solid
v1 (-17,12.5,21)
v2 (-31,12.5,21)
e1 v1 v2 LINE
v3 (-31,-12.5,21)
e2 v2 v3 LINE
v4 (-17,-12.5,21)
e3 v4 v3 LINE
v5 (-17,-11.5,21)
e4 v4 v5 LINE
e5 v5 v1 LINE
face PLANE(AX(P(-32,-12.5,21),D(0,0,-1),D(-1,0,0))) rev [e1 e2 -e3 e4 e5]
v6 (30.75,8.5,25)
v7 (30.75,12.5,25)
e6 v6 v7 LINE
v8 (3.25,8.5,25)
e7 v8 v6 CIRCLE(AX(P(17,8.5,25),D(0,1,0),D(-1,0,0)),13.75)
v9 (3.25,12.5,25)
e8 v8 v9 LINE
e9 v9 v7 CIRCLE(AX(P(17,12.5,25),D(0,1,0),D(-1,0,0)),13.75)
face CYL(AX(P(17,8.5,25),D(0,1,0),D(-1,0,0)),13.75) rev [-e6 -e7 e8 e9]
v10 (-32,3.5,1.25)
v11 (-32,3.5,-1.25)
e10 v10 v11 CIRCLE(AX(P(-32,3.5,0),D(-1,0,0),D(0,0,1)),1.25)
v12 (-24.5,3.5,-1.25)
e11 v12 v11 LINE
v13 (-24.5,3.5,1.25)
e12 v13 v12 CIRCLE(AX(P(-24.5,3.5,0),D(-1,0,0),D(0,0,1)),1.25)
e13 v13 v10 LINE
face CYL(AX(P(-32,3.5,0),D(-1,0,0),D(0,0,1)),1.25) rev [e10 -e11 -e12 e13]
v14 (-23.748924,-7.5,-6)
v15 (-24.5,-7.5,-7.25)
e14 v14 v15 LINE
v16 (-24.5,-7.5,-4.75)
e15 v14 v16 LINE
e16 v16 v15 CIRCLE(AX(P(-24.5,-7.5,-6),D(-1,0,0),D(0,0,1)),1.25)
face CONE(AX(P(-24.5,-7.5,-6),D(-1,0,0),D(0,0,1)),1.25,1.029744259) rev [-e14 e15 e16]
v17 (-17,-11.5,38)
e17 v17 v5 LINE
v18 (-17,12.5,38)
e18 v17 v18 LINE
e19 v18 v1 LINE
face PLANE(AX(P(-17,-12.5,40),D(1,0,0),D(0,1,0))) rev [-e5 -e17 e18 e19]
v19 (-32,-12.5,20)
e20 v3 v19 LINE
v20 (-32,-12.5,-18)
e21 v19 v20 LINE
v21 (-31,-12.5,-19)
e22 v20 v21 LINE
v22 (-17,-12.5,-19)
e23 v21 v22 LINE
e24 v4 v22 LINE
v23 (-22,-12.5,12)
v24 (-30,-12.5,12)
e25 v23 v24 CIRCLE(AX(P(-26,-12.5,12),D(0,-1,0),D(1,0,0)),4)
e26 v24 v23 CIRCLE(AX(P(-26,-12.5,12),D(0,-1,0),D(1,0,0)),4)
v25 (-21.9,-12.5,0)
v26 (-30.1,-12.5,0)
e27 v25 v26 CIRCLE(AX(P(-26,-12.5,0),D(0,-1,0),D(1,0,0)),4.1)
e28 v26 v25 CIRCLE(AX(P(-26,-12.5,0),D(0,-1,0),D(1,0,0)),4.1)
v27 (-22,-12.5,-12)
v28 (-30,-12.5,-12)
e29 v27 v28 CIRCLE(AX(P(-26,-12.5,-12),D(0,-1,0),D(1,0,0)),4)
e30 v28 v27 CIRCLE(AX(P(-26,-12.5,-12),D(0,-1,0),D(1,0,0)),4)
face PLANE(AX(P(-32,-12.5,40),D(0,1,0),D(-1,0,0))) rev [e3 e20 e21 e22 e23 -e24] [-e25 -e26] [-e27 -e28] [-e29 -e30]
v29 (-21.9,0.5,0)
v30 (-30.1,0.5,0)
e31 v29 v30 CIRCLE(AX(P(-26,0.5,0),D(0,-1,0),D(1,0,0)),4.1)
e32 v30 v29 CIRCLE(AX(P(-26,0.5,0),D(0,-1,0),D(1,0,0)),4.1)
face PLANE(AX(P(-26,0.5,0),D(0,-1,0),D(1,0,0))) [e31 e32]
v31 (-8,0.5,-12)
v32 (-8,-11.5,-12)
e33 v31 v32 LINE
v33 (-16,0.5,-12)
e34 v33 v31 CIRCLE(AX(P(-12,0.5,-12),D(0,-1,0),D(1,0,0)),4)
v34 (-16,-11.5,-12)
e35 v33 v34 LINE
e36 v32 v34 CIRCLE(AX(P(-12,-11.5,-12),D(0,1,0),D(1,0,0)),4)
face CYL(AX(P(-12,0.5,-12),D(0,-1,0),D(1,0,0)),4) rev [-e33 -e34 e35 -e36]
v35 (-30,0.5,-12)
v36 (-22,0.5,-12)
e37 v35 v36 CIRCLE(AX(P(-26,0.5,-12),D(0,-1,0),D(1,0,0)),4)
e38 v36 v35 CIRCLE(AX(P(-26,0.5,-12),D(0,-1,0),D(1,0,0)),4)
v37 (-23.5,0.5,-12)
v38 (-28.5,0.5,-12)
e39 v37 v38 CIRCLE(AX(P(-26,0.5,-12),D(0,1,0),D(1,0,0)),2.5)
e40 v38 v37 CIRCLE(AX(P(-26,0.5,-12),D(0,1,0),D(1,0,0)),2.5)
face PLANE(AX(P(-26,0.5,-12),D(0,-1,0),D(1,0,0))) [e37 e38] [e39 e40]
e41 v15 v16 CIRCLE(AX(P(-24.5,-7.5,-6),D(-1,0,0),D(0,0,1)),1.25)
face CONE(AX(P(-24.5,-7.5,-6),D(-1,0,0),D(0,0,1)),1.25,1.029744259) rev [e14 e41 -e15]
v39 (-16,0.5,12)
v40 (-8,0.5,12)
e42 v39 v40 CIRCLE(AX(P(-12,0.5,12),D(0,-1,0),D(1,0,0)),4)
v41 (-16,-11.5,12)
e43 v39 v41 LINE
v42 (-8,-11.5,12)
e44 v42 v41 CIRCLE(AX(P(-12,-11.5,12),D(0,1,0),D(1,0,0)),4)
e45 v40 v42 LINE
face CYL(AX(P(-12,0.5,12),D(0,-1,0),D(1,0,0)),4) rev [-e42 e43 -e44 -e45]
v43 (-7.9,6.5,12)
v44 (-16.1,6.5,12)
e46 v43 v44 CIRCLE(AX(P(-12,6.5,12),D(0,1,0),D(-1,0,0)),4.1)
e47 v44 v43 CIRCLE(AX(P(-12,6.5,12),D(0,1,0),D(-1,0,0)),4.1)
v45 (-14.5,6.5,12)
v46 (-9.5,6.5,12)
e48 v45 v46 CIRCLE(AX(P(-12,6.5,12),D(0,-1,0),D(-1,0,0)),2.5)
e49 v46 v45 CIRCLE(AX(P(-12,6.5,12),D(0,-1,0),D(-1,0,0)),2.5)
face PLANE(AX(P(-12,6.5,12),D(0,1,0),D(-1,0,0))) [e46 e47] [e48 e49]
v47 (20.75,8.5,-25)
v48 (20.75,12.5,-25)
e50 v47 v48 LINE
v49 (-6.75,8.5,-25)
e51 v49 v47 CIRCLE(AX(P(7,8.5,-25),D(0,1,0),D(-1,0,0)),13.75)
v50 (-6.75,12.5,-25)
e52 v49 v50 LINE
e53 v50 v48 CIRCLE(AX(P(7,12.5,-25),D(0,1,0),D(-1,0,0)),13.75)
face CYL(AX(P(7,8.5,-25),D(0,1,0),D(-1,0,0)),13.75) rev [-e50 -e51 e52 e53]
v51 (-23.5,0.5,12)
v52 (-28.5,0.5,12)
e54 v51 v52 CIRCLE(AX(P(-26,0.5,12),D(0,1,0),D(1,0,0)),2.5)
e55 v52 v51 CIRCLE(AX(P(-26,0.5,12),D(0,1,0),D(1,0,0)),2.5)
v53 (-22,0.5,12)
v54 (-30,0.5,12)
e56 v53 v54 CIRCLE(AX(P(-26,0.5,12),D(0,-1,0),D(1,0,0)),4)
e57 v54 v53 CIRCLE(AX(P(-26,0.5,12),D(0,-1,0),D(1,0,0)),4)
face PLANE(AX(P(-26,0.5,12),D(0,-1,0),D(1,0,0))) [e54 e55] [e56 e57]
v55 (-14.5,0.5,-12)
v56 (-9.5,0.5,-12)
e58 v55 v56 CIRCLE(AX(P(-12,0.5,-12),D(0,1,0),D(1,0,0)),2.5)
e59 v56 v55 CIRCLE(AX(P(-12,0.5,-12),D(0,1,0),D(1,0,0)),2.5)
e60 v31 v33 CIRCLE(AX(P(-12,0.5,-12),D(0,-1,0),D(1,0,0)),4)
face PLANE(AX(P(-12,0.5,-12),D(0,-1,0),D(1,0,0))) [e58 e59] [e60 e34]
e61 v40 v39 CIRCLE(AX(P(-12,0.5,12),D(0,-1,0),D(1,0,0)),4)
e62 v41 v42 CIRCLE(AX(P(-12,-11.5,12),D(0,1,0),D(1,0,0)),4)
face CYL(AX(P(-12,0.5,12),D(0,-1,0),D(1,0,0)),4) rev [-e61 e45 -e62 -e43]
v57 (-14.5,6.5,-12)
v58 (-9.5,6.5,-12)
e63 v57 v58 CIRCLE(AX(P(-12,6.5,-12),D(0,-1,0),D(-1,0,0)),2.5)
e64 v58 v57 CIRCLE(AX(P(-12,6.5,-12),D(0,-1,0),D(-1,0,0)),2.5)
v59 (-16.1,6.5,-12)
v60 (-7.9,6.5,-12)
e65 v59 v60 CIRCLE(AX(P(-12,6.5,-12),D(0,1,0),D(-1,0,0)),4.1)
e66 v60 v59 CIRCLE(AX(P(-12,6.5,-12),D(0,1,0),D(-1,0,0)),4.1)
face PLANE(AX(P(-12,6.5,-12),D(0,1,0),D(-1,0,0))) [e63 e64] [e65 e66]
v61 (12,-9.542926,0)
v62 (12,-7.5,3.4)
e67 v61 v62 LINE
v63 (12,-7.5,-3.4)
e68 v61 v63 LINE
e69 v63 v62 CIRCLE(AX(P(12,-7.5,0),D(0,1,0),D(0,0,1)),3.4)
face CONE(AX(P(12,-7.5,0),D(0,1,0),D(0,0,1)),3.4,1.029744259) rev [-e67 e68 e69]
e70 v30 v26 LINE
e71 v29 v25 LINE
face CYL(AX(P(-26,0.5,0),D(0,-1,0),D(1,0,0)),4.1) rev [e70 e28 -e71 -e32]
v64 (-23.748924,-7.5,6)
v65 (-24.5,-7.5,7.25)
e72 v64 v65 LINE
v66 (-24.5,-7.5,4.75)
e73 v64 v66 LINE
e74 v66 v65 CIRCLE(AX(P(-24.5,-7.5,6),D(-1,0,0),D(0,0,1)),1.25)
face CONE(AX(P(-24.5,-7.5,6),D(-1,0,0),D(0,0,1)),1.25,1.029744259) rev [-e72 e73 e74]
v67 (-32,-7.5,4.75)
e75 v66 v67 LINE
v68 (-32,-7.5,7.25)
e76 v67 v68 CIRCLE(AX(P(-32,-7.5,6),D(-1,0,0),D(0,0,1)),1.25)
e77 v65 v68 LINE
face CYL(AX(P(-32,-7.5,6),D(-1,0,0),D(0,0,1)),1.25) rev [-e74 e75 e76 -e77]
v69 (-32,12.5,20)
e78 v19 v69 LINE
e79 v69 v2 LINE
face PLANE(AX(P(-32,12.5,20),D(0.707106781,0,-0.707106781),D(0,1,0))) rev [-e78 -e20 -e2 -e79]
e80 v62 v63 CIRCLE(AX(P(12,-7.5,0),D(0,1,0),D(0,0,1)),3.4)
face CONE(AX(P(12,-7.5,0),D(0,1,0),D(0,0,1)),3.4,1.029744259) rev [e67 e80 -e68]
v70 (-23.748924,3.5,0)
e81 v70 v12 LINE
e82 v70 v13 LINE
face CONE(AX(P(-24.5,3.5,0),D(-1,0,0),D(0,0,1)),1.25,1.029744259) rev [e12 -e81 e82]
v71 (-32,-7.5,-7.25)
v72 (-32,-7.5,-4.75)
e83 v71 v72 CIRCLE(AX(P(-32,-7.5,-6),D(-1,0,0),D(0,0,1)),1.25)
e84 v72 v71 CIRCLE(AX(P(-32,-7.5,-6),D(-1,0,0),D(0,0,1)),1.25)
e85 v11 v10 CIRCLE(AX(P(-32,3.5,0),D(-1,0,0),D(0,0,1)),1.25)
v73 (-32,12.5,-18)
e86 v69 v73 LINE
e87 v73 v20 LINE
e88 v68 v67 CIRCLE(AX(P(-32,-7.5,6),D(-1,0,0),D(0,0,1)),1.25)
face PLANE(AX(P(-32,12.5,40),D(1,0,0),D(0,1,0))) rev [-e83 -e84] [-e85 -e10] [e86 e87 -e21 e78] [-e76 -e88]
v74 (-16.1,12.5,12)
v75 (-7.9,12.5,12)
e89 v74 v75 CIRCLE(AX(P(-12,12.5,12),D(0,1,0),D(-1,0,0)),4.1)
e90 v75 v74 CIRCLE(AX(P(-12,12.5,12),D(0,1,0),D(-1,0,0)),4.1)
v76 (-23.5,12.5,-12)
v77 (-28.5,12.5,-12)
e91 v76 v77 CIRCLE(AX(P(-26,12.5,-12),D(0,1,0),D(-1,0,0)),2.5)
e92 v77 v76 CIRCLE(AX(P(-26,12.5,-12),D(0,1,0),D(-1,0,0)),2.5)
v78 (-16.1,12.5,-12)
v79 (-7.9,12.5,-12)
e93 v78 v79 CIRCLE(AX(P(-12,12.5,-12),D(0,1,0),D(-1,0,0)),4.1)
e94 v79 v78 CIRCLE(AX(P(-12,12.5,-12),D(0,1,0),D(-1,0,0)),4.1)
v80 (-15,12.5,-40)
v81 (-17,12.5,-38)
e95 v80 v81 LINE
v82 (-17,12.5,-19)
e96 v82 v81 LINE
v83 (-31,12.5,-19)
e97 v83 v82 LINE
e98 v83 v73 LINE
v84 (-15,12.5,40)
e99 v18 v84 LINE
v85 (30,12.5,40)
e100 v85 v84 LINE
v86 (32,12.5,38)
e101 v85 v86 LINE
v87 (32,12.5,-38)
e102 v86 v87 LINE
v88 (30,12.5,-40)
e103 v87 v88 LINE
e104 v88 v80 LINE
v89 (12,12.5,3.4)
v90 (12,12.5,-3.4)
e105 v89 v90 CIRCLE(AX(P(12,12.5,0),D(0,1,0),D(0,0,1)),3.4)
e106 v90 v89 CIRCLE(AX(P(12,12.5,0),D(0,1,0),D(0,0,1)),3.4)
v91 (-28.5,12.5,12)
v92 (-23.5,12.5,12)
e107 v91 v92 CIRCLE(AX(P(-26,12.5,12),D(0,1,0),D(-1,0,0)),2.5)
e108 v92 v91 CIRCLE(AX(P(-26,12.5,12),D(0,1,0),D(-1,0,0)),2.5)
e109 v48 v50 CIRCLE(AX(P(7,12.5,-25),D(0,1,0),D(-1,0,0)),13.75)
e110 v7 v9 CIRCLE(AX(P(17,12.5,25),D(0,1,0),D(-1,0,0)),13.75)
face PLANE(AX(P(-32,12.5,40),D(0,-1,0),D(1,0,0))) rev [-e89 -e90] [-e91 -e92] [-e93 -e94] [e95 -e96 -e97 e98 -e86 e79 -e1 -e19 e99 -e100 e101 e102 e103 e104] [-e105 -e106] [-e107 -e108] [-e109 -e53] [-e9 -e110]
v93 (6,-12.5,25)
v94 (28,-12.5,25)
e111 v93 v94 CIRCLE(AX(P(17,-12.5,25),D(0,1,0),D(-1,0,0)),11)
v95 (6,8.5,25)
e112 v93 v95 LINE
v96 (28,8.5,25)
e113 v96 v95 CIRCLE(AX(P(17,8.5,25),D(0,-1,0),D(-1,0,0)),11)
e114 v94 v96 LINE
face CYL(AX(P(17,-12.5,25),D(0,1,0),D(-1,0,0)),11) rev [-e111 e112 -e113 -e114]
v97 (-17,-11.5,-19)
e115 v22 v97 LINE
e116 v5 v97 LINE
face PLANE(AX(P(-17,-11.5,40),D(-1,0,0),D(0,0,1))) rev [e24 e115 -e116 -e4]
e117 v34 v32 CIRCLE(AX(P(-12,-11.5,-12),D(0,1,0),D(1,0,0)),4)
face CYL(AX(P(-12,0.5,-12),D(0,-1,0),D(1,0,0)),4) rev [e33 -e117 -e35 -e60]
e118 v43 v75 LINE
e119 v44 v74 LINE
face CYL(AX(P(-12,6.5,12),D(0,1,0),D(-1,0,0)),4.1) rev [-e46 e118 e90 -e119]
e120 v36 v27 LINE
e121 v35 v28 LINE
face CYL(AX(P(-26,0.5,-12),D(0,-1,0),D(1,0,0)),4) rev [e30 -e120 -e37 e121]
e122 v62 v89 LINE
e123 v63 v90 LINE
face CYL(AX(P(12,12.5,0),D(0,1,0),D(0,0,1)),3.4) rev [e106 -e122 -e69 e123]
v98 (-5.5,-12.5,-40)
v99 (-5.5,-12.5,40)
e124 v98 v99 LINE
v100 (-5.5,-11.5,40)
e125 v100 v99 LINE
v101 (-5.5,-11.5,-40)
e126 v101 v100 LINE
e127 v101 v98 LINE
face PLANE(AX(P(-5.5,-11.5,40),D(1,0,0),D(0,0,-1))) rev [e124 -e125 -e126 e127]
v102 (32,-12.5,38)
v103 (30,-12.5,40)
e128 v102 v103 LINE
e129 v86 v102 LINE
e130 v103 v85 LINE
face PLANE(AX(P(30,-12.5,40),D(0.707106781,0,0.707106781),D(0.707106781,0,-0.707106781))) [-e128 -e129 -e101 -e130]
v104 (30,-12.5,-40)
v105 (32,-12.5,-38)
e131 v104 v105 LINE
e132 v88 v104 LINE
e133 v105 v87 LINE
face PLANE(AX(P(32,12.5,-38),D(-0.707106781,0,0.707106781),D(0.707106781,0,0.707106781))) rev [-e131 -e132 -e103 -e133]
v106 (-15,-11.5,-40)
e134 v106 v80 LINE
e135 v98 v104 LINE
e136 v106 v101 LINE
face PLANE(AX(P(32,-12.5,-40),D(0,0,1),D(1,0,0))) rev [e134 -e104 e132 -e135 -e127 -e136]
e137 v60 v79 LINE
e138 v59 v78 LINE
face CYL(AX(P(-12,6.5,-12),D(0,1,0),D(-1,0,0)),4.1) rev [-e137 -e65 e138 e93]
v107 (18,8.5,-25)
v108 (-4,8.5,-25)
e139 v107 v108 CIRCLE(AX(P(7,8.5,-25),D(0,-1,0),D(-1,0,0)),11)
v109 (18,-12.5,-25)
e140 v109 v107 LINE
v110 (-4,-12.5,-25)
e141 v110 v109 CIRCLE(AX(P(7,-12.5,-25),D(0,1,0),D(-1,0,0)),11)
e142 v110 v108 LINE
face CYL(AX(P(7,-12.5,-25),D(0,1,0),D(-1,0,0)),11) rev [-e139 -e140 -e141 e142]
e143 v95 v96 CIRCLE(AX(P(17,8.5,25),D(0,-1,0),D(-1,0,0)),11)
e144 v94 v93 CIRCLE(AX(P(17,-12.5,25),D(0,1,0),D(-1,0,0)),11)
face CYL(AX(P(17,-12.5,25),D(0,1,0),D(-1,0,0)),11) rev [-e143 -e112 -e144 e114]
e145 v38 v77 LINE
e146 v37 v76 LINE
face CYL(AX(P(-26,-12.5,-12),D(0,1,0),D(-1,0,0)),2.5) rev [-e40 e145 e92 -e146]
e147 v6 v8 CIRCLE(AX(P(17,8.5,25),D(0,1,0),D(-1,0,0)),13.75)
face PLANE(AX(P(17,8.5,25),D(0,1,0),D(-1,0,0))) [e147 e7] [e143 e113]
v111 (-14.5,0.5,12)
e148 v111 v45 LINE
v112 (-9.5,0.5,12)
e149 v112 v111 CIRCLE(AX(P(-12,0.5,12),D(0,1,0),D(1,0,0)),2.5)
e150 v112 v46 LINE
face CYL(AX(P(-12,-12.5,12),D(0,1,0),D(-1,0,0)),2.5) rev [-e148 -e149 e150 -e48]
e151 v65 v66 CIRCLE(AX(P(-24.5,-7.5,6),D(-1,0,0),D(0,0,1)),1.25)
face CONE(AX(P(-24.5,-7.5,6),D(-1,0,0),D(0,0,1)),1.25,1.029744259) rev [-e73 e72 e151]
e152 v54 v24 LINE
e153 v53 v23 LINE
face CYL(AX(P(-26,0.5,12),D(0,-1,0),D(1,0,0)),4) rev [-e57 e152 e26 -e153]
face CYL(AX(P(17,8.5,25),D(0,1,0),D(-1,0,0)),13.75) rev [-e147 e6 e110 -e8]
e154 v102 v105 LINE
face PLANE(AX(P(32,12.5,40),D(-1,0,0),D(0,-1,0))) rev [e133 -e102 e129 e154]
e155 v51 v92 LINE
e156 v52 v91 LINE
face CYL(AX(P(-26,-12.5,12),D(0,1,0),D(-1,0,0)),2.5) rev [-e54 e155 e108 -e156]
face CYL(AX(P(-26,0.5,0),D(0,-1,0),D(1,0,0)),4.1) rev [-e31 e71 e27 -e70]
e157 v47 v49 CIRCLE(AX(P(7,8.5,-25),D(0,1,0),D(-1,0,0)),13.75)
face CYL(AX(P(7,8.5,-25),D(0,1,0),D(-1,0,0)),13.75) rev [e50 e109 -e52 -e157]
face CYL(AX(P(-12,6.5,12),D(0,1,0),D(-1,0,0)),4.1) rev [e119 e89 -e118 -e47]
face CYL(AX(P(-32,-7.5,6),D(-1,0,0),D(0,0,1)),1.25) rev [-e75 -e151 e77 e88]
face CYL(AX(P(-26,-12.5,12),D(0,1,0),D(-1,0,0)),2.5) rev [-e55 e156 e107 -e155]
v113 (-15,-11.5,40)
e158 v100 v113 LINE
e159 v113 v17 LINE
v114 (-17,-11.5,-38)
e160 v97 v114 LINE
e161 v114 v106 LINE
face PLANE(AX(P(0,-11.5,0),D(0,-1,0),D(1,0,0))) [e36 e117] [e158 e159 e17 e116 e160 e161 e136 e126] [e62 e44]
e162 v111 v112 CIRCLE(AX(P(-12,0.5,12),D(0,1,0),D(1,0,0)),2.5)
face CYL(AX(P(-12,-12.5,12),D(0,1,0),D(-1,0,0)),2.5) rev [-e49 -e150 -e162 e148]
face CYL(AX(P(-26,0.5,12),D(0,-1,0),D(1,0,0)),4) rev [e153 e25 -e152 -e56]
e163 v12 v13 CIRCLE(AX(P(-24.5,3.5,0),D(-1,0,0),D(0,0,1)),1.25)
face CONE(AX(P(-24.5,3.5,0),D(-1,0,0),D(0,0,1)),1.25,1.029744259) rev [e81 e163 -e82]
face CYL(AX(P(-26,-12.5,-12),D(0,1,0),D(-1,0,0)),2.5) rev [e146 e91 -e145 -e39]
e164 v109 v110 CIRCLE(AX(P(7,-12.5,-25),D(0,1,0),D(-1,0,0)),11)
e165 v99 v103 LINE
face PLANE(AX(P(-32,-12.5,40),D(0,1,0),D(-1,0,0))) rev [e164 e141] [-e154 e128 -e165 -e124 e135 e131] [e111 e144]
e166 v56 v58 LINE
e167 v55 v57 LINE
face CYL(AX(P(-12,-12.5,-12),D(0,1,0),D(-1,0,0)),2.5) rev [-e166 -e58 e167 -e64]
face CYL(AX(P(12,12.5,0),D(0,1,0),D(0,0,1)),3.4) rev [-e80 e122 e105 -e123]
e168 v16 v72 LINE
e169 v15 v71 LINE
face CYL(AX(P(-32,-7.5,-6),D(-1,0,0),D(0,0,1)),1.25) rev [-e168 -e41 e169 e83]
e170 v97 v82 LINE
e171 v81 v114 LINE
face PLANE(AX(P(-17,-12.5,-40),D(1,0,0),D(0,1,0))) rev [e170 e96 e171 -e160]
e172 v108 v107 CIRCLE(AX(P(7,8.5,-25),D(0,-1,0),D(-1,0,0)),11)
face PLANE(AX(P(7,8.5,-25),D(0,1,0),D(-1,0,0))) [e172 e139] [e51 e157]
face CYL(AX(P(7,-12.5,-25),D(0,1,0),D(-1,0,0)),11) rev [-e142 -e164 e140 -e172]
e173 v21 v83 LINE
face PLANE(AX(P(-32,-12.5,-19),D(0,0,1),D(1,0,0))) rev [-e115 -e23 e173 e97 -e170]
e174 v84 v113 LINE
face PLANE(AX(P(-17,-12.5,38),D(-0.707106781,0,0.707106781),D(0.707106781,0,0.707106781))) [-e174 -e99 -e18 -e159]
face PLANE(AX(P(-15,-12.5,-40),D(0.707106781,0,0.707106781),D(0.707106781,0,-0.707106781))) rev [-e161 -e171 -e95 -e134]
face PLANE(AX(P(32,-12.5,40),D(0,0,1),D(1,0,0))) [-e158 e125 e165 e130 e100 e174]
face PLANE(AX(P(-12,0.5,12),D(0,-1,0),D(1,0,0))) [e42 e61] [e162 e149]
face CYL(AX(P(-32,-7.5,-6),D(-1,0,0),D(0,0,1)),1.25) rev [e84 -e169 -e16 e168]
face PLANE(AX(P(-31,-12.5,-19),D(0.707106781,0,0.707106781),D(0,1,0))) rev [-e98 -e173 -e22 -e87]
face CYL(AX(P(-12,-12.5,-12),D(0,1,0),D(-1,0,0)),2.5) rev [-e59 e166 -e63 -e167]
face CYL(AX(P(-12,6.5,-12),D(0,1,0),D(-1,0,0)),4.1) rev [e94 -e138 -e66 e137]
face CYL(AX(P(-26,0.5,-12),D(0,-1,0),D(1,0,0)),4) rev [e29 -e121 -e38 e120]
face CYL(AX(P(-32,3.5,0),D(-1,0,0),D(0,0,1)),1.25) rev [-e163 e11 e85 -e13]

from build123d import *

# Parameters (mm, degrees)
SKETCH1_W             = 64
SKETCH1_H             = 25
BOSS_EXTRUDE1_DEPTH   = 40
SKETCH3_R             = 11
SKETCH3_R_2           = 2.5
CUT_EXTRUDE1_DEPTH    = 58
M3_TAPPED_HOLE1_D     = 2.5
M3_TAPPED_HOLE1_DEPTH = 7.5
M3_TAPPED_HOLE1_TIP   = 0.751075774
M8_TAPPED_HOLE1_D     = 6.8
M8_TAPPED_HOLE1_DEPTH = 20
M8_TAPPED_HOLE1_TIP   = 2.042926105
SKETCH11_W            = 15
SKETCH11_H            = 21
SKETCH11_H_2          = 19
CUT_EXTRUDE5_DEPTH    = 58
SKETCH13_R            = 4
SKETCH13_R_2          = 4.1
CUT_EXTRUDE7_DEPTH    = 13
SKETCH14_R            = 4.1
CUT_EXTRUDE8_DEPTH    = 6
SKETCH15_W            = 11.5
SKETCH15_H            = 80
CUT_EXTRUDE11_DEPTH   = 1
SKETCH16_R            = 13.75
CUT_EXTRUDE12_DEPTH   = 4
CHAMFER2_SIZE         = 2
CHAMFER3_SIZE         = 1


with BuildPart() as part:
    # Sketch1 → Boss-Extrude1 (new, symmetric)
    with BuildSketch(Plane.XY):
        Rectangle(SKETCH1_W, SKETCH1_H)
    extrude(amount=BOSS_EXTRUDE1_DEPTH, both=True)

    # Sketch3 → Cut-Extrude1 (cut, through all)
    with BuildSketch(Plane(origin=(0, 12.5, 0), x_dir=(1, 0, 0), z_dir=(0, 1, 0))):
        with Locations(Location((7, 25, 0), (0, 0, 180))):
            Circle(SKETCH3_R)
        with Locations(Location((17, -25, 0), (0, 0, 180))):
            Circle(SKETCH3_R)
        with Locations(Location((-12, 12, 0), (0, 0, 180))):
            Circle(SKETCH3_R_2)
        with Locations(Location((-12, -12, 0), (0, 0, 180))):
            Circle(SKETCH3_R_2)
        with Locations(Location((-26, 12, 0), (0, 0, 180))):
            Circle(SKETCH3_R_2)
        with Locations(Location((-26, -12, 0), (0, 0, 180))):
            Circle(SKETCH3_R_2)
    extrude(amount=-CUT_EXTRUDE1_DEPTH, mode=Mode.SUBTRACT)

    # M3 Tapped Hole1
    with Locations(Plane.ZY.offset(32)):
        with Locations((0, 3.5), (-6, -7.5), (6, -7.5)):
            Hole(M3_TAPPED_HOLE1_D / 2, depth=M3_TAPPED_HOLE1_DEPTH)
            with Locations((0, 0, -(M3_TAPPED_HOLE1_DEPTH + M3_TAPPED_HOLE1_TIP / 2))):  # 118° drill point
                Cone(0, M3_TAPPED_HOLE1_D / 2, M3_TAPPED_HOLE1_TIP, mode=Mode.SUBTRACT)

    # M8 Tapped Hole1
    with Locations(Plane(origin=(0, 12.5, 0), x_dir=(-1, 0, 0), z_dir=(0, 1, 0))):
        with Locations((-12, 0)):
            Hole(M8_TAPPED_HOLE1_D / 2, depth=M8_TAPPED_HOLE1_DEPTH)
            with Locations((0, 0, -(M8_TAPPED_HOLE1_DEPTH + M8_TAPPED_HOLE1_TIP / 2))):  # 118° drill point
                Cone(0, M8_TAPPED_HOLE1_D / 2, M8_TAPPED_HOLE1_TIP, mode=Mode.SUBTRACT)

    # Sketch11 → Cut-Extrude5 (cut, through all)
    with BuildSketch(Plane(origin=(0, 12.5, 0), x_dir=(1, 0, 0), z_dir=(0, 1, 0))):
        with Locations((-24.5, 29.5)):
            Rectangle(SKETCH11_W, SKETCH11_H)
        with Locations((-24.5, -30.5)):
            Rectangle(SKETCH11_W, SKETCH11_H_2)
    extrude(amount=-CUT_EXTRUDE5_DEPTH, mode=Mode.SUBTRACT)

    # Sketch13 → Cut-Extrude7 (cut)
    with BuildSketch(Plane.XZ.offset(12.5)):
        with Locations((-26, -12)):
            Circle(SKETCH13_R)
        with Locations((-26, 12)):
            Circle(SKETCH13_R)
        with Locations((-12, 12)):
            Circle(SKETCH13_R)
        with Locations((-12, -12)):
            Circle(SKETCH13_R)
        with Locations((-26, 0)):
            Circle(SKETCH13_R_2)
    extrude(amount=-CUT_EXTRUDE7_DEPTH, mode=Mode.SUBTRACT)

    # Sketch14 → Cut-Extrude8 (cut)
    with BuildSketch(Plane(origin=(0, 12.5, 0), x_dir=(1, 0, 0), z_dir=(0, 1, 0))):
        with Locations(Location((-12, -12, 0), (0, 0, 180))):
            Circle(SKETCH14_R)
        with Locations(Location((-12, 12, 0), (0, 0, 180))):
            Circle(SKETCH14_R)
    extrude(amount=-CUT_EXTRUDE8_DEPTH, mode=Mode.SUBTRACT)

    # Sketch15 → Cut-Extrude11 (cut)
    with BuildSketch(Plane(origin=(0, -12.5, 0), x_dir=(-1, 0, 0), z_dir=(0, -1, 0))):
        with Locations((11.25, 0)):
            Rectangle(SKETCH15_W, SKETCH15_H)
    extrude(amount=-CUT_EXTRUDE11_DEPTH, mode=Mode.SUBTRACT)

    # Sketch16 → Cut-Extrude12 (cut)
    with BuildSketch(Plane(origin=(0, 12.5, 0), x_dir=(1, 0, 0), z_dir=(0, 1, 0))):
        with Locations(Location((17, -25, 0), (0, 0, 180))):
            Circle(SKETCH16_R)
        with Locations(Location((7, 25, 0), (0, 0, 180))):
            Circle(SKETCH16_R)
    extrude(amount=-CUT_EXTRUDE12_DEPTH, mode=Mode.SUBTRACT)

    # Chamfer2
    chamfer2_edges = [part.edges().sort_by_distance(p)[0] for p in [
        (-17, 0.5, 40),
        (-17, 0.5, -40),
        (32, 0, 40),
        (32, 0, -40),
    ]]
    chamfer(chamfer2_edges, length=CHAMFER2_SIZE)

    # Chamfer3
    chamfer3_edges = [part.edges().sort_by_distance(p)[0] for p in [
        (-32, 0, -19),
        (-32, 0, 21),
    ]]
    chamfer(chamfer3_edges, length=CHAMFER3_SIZE)


solid = part.part
